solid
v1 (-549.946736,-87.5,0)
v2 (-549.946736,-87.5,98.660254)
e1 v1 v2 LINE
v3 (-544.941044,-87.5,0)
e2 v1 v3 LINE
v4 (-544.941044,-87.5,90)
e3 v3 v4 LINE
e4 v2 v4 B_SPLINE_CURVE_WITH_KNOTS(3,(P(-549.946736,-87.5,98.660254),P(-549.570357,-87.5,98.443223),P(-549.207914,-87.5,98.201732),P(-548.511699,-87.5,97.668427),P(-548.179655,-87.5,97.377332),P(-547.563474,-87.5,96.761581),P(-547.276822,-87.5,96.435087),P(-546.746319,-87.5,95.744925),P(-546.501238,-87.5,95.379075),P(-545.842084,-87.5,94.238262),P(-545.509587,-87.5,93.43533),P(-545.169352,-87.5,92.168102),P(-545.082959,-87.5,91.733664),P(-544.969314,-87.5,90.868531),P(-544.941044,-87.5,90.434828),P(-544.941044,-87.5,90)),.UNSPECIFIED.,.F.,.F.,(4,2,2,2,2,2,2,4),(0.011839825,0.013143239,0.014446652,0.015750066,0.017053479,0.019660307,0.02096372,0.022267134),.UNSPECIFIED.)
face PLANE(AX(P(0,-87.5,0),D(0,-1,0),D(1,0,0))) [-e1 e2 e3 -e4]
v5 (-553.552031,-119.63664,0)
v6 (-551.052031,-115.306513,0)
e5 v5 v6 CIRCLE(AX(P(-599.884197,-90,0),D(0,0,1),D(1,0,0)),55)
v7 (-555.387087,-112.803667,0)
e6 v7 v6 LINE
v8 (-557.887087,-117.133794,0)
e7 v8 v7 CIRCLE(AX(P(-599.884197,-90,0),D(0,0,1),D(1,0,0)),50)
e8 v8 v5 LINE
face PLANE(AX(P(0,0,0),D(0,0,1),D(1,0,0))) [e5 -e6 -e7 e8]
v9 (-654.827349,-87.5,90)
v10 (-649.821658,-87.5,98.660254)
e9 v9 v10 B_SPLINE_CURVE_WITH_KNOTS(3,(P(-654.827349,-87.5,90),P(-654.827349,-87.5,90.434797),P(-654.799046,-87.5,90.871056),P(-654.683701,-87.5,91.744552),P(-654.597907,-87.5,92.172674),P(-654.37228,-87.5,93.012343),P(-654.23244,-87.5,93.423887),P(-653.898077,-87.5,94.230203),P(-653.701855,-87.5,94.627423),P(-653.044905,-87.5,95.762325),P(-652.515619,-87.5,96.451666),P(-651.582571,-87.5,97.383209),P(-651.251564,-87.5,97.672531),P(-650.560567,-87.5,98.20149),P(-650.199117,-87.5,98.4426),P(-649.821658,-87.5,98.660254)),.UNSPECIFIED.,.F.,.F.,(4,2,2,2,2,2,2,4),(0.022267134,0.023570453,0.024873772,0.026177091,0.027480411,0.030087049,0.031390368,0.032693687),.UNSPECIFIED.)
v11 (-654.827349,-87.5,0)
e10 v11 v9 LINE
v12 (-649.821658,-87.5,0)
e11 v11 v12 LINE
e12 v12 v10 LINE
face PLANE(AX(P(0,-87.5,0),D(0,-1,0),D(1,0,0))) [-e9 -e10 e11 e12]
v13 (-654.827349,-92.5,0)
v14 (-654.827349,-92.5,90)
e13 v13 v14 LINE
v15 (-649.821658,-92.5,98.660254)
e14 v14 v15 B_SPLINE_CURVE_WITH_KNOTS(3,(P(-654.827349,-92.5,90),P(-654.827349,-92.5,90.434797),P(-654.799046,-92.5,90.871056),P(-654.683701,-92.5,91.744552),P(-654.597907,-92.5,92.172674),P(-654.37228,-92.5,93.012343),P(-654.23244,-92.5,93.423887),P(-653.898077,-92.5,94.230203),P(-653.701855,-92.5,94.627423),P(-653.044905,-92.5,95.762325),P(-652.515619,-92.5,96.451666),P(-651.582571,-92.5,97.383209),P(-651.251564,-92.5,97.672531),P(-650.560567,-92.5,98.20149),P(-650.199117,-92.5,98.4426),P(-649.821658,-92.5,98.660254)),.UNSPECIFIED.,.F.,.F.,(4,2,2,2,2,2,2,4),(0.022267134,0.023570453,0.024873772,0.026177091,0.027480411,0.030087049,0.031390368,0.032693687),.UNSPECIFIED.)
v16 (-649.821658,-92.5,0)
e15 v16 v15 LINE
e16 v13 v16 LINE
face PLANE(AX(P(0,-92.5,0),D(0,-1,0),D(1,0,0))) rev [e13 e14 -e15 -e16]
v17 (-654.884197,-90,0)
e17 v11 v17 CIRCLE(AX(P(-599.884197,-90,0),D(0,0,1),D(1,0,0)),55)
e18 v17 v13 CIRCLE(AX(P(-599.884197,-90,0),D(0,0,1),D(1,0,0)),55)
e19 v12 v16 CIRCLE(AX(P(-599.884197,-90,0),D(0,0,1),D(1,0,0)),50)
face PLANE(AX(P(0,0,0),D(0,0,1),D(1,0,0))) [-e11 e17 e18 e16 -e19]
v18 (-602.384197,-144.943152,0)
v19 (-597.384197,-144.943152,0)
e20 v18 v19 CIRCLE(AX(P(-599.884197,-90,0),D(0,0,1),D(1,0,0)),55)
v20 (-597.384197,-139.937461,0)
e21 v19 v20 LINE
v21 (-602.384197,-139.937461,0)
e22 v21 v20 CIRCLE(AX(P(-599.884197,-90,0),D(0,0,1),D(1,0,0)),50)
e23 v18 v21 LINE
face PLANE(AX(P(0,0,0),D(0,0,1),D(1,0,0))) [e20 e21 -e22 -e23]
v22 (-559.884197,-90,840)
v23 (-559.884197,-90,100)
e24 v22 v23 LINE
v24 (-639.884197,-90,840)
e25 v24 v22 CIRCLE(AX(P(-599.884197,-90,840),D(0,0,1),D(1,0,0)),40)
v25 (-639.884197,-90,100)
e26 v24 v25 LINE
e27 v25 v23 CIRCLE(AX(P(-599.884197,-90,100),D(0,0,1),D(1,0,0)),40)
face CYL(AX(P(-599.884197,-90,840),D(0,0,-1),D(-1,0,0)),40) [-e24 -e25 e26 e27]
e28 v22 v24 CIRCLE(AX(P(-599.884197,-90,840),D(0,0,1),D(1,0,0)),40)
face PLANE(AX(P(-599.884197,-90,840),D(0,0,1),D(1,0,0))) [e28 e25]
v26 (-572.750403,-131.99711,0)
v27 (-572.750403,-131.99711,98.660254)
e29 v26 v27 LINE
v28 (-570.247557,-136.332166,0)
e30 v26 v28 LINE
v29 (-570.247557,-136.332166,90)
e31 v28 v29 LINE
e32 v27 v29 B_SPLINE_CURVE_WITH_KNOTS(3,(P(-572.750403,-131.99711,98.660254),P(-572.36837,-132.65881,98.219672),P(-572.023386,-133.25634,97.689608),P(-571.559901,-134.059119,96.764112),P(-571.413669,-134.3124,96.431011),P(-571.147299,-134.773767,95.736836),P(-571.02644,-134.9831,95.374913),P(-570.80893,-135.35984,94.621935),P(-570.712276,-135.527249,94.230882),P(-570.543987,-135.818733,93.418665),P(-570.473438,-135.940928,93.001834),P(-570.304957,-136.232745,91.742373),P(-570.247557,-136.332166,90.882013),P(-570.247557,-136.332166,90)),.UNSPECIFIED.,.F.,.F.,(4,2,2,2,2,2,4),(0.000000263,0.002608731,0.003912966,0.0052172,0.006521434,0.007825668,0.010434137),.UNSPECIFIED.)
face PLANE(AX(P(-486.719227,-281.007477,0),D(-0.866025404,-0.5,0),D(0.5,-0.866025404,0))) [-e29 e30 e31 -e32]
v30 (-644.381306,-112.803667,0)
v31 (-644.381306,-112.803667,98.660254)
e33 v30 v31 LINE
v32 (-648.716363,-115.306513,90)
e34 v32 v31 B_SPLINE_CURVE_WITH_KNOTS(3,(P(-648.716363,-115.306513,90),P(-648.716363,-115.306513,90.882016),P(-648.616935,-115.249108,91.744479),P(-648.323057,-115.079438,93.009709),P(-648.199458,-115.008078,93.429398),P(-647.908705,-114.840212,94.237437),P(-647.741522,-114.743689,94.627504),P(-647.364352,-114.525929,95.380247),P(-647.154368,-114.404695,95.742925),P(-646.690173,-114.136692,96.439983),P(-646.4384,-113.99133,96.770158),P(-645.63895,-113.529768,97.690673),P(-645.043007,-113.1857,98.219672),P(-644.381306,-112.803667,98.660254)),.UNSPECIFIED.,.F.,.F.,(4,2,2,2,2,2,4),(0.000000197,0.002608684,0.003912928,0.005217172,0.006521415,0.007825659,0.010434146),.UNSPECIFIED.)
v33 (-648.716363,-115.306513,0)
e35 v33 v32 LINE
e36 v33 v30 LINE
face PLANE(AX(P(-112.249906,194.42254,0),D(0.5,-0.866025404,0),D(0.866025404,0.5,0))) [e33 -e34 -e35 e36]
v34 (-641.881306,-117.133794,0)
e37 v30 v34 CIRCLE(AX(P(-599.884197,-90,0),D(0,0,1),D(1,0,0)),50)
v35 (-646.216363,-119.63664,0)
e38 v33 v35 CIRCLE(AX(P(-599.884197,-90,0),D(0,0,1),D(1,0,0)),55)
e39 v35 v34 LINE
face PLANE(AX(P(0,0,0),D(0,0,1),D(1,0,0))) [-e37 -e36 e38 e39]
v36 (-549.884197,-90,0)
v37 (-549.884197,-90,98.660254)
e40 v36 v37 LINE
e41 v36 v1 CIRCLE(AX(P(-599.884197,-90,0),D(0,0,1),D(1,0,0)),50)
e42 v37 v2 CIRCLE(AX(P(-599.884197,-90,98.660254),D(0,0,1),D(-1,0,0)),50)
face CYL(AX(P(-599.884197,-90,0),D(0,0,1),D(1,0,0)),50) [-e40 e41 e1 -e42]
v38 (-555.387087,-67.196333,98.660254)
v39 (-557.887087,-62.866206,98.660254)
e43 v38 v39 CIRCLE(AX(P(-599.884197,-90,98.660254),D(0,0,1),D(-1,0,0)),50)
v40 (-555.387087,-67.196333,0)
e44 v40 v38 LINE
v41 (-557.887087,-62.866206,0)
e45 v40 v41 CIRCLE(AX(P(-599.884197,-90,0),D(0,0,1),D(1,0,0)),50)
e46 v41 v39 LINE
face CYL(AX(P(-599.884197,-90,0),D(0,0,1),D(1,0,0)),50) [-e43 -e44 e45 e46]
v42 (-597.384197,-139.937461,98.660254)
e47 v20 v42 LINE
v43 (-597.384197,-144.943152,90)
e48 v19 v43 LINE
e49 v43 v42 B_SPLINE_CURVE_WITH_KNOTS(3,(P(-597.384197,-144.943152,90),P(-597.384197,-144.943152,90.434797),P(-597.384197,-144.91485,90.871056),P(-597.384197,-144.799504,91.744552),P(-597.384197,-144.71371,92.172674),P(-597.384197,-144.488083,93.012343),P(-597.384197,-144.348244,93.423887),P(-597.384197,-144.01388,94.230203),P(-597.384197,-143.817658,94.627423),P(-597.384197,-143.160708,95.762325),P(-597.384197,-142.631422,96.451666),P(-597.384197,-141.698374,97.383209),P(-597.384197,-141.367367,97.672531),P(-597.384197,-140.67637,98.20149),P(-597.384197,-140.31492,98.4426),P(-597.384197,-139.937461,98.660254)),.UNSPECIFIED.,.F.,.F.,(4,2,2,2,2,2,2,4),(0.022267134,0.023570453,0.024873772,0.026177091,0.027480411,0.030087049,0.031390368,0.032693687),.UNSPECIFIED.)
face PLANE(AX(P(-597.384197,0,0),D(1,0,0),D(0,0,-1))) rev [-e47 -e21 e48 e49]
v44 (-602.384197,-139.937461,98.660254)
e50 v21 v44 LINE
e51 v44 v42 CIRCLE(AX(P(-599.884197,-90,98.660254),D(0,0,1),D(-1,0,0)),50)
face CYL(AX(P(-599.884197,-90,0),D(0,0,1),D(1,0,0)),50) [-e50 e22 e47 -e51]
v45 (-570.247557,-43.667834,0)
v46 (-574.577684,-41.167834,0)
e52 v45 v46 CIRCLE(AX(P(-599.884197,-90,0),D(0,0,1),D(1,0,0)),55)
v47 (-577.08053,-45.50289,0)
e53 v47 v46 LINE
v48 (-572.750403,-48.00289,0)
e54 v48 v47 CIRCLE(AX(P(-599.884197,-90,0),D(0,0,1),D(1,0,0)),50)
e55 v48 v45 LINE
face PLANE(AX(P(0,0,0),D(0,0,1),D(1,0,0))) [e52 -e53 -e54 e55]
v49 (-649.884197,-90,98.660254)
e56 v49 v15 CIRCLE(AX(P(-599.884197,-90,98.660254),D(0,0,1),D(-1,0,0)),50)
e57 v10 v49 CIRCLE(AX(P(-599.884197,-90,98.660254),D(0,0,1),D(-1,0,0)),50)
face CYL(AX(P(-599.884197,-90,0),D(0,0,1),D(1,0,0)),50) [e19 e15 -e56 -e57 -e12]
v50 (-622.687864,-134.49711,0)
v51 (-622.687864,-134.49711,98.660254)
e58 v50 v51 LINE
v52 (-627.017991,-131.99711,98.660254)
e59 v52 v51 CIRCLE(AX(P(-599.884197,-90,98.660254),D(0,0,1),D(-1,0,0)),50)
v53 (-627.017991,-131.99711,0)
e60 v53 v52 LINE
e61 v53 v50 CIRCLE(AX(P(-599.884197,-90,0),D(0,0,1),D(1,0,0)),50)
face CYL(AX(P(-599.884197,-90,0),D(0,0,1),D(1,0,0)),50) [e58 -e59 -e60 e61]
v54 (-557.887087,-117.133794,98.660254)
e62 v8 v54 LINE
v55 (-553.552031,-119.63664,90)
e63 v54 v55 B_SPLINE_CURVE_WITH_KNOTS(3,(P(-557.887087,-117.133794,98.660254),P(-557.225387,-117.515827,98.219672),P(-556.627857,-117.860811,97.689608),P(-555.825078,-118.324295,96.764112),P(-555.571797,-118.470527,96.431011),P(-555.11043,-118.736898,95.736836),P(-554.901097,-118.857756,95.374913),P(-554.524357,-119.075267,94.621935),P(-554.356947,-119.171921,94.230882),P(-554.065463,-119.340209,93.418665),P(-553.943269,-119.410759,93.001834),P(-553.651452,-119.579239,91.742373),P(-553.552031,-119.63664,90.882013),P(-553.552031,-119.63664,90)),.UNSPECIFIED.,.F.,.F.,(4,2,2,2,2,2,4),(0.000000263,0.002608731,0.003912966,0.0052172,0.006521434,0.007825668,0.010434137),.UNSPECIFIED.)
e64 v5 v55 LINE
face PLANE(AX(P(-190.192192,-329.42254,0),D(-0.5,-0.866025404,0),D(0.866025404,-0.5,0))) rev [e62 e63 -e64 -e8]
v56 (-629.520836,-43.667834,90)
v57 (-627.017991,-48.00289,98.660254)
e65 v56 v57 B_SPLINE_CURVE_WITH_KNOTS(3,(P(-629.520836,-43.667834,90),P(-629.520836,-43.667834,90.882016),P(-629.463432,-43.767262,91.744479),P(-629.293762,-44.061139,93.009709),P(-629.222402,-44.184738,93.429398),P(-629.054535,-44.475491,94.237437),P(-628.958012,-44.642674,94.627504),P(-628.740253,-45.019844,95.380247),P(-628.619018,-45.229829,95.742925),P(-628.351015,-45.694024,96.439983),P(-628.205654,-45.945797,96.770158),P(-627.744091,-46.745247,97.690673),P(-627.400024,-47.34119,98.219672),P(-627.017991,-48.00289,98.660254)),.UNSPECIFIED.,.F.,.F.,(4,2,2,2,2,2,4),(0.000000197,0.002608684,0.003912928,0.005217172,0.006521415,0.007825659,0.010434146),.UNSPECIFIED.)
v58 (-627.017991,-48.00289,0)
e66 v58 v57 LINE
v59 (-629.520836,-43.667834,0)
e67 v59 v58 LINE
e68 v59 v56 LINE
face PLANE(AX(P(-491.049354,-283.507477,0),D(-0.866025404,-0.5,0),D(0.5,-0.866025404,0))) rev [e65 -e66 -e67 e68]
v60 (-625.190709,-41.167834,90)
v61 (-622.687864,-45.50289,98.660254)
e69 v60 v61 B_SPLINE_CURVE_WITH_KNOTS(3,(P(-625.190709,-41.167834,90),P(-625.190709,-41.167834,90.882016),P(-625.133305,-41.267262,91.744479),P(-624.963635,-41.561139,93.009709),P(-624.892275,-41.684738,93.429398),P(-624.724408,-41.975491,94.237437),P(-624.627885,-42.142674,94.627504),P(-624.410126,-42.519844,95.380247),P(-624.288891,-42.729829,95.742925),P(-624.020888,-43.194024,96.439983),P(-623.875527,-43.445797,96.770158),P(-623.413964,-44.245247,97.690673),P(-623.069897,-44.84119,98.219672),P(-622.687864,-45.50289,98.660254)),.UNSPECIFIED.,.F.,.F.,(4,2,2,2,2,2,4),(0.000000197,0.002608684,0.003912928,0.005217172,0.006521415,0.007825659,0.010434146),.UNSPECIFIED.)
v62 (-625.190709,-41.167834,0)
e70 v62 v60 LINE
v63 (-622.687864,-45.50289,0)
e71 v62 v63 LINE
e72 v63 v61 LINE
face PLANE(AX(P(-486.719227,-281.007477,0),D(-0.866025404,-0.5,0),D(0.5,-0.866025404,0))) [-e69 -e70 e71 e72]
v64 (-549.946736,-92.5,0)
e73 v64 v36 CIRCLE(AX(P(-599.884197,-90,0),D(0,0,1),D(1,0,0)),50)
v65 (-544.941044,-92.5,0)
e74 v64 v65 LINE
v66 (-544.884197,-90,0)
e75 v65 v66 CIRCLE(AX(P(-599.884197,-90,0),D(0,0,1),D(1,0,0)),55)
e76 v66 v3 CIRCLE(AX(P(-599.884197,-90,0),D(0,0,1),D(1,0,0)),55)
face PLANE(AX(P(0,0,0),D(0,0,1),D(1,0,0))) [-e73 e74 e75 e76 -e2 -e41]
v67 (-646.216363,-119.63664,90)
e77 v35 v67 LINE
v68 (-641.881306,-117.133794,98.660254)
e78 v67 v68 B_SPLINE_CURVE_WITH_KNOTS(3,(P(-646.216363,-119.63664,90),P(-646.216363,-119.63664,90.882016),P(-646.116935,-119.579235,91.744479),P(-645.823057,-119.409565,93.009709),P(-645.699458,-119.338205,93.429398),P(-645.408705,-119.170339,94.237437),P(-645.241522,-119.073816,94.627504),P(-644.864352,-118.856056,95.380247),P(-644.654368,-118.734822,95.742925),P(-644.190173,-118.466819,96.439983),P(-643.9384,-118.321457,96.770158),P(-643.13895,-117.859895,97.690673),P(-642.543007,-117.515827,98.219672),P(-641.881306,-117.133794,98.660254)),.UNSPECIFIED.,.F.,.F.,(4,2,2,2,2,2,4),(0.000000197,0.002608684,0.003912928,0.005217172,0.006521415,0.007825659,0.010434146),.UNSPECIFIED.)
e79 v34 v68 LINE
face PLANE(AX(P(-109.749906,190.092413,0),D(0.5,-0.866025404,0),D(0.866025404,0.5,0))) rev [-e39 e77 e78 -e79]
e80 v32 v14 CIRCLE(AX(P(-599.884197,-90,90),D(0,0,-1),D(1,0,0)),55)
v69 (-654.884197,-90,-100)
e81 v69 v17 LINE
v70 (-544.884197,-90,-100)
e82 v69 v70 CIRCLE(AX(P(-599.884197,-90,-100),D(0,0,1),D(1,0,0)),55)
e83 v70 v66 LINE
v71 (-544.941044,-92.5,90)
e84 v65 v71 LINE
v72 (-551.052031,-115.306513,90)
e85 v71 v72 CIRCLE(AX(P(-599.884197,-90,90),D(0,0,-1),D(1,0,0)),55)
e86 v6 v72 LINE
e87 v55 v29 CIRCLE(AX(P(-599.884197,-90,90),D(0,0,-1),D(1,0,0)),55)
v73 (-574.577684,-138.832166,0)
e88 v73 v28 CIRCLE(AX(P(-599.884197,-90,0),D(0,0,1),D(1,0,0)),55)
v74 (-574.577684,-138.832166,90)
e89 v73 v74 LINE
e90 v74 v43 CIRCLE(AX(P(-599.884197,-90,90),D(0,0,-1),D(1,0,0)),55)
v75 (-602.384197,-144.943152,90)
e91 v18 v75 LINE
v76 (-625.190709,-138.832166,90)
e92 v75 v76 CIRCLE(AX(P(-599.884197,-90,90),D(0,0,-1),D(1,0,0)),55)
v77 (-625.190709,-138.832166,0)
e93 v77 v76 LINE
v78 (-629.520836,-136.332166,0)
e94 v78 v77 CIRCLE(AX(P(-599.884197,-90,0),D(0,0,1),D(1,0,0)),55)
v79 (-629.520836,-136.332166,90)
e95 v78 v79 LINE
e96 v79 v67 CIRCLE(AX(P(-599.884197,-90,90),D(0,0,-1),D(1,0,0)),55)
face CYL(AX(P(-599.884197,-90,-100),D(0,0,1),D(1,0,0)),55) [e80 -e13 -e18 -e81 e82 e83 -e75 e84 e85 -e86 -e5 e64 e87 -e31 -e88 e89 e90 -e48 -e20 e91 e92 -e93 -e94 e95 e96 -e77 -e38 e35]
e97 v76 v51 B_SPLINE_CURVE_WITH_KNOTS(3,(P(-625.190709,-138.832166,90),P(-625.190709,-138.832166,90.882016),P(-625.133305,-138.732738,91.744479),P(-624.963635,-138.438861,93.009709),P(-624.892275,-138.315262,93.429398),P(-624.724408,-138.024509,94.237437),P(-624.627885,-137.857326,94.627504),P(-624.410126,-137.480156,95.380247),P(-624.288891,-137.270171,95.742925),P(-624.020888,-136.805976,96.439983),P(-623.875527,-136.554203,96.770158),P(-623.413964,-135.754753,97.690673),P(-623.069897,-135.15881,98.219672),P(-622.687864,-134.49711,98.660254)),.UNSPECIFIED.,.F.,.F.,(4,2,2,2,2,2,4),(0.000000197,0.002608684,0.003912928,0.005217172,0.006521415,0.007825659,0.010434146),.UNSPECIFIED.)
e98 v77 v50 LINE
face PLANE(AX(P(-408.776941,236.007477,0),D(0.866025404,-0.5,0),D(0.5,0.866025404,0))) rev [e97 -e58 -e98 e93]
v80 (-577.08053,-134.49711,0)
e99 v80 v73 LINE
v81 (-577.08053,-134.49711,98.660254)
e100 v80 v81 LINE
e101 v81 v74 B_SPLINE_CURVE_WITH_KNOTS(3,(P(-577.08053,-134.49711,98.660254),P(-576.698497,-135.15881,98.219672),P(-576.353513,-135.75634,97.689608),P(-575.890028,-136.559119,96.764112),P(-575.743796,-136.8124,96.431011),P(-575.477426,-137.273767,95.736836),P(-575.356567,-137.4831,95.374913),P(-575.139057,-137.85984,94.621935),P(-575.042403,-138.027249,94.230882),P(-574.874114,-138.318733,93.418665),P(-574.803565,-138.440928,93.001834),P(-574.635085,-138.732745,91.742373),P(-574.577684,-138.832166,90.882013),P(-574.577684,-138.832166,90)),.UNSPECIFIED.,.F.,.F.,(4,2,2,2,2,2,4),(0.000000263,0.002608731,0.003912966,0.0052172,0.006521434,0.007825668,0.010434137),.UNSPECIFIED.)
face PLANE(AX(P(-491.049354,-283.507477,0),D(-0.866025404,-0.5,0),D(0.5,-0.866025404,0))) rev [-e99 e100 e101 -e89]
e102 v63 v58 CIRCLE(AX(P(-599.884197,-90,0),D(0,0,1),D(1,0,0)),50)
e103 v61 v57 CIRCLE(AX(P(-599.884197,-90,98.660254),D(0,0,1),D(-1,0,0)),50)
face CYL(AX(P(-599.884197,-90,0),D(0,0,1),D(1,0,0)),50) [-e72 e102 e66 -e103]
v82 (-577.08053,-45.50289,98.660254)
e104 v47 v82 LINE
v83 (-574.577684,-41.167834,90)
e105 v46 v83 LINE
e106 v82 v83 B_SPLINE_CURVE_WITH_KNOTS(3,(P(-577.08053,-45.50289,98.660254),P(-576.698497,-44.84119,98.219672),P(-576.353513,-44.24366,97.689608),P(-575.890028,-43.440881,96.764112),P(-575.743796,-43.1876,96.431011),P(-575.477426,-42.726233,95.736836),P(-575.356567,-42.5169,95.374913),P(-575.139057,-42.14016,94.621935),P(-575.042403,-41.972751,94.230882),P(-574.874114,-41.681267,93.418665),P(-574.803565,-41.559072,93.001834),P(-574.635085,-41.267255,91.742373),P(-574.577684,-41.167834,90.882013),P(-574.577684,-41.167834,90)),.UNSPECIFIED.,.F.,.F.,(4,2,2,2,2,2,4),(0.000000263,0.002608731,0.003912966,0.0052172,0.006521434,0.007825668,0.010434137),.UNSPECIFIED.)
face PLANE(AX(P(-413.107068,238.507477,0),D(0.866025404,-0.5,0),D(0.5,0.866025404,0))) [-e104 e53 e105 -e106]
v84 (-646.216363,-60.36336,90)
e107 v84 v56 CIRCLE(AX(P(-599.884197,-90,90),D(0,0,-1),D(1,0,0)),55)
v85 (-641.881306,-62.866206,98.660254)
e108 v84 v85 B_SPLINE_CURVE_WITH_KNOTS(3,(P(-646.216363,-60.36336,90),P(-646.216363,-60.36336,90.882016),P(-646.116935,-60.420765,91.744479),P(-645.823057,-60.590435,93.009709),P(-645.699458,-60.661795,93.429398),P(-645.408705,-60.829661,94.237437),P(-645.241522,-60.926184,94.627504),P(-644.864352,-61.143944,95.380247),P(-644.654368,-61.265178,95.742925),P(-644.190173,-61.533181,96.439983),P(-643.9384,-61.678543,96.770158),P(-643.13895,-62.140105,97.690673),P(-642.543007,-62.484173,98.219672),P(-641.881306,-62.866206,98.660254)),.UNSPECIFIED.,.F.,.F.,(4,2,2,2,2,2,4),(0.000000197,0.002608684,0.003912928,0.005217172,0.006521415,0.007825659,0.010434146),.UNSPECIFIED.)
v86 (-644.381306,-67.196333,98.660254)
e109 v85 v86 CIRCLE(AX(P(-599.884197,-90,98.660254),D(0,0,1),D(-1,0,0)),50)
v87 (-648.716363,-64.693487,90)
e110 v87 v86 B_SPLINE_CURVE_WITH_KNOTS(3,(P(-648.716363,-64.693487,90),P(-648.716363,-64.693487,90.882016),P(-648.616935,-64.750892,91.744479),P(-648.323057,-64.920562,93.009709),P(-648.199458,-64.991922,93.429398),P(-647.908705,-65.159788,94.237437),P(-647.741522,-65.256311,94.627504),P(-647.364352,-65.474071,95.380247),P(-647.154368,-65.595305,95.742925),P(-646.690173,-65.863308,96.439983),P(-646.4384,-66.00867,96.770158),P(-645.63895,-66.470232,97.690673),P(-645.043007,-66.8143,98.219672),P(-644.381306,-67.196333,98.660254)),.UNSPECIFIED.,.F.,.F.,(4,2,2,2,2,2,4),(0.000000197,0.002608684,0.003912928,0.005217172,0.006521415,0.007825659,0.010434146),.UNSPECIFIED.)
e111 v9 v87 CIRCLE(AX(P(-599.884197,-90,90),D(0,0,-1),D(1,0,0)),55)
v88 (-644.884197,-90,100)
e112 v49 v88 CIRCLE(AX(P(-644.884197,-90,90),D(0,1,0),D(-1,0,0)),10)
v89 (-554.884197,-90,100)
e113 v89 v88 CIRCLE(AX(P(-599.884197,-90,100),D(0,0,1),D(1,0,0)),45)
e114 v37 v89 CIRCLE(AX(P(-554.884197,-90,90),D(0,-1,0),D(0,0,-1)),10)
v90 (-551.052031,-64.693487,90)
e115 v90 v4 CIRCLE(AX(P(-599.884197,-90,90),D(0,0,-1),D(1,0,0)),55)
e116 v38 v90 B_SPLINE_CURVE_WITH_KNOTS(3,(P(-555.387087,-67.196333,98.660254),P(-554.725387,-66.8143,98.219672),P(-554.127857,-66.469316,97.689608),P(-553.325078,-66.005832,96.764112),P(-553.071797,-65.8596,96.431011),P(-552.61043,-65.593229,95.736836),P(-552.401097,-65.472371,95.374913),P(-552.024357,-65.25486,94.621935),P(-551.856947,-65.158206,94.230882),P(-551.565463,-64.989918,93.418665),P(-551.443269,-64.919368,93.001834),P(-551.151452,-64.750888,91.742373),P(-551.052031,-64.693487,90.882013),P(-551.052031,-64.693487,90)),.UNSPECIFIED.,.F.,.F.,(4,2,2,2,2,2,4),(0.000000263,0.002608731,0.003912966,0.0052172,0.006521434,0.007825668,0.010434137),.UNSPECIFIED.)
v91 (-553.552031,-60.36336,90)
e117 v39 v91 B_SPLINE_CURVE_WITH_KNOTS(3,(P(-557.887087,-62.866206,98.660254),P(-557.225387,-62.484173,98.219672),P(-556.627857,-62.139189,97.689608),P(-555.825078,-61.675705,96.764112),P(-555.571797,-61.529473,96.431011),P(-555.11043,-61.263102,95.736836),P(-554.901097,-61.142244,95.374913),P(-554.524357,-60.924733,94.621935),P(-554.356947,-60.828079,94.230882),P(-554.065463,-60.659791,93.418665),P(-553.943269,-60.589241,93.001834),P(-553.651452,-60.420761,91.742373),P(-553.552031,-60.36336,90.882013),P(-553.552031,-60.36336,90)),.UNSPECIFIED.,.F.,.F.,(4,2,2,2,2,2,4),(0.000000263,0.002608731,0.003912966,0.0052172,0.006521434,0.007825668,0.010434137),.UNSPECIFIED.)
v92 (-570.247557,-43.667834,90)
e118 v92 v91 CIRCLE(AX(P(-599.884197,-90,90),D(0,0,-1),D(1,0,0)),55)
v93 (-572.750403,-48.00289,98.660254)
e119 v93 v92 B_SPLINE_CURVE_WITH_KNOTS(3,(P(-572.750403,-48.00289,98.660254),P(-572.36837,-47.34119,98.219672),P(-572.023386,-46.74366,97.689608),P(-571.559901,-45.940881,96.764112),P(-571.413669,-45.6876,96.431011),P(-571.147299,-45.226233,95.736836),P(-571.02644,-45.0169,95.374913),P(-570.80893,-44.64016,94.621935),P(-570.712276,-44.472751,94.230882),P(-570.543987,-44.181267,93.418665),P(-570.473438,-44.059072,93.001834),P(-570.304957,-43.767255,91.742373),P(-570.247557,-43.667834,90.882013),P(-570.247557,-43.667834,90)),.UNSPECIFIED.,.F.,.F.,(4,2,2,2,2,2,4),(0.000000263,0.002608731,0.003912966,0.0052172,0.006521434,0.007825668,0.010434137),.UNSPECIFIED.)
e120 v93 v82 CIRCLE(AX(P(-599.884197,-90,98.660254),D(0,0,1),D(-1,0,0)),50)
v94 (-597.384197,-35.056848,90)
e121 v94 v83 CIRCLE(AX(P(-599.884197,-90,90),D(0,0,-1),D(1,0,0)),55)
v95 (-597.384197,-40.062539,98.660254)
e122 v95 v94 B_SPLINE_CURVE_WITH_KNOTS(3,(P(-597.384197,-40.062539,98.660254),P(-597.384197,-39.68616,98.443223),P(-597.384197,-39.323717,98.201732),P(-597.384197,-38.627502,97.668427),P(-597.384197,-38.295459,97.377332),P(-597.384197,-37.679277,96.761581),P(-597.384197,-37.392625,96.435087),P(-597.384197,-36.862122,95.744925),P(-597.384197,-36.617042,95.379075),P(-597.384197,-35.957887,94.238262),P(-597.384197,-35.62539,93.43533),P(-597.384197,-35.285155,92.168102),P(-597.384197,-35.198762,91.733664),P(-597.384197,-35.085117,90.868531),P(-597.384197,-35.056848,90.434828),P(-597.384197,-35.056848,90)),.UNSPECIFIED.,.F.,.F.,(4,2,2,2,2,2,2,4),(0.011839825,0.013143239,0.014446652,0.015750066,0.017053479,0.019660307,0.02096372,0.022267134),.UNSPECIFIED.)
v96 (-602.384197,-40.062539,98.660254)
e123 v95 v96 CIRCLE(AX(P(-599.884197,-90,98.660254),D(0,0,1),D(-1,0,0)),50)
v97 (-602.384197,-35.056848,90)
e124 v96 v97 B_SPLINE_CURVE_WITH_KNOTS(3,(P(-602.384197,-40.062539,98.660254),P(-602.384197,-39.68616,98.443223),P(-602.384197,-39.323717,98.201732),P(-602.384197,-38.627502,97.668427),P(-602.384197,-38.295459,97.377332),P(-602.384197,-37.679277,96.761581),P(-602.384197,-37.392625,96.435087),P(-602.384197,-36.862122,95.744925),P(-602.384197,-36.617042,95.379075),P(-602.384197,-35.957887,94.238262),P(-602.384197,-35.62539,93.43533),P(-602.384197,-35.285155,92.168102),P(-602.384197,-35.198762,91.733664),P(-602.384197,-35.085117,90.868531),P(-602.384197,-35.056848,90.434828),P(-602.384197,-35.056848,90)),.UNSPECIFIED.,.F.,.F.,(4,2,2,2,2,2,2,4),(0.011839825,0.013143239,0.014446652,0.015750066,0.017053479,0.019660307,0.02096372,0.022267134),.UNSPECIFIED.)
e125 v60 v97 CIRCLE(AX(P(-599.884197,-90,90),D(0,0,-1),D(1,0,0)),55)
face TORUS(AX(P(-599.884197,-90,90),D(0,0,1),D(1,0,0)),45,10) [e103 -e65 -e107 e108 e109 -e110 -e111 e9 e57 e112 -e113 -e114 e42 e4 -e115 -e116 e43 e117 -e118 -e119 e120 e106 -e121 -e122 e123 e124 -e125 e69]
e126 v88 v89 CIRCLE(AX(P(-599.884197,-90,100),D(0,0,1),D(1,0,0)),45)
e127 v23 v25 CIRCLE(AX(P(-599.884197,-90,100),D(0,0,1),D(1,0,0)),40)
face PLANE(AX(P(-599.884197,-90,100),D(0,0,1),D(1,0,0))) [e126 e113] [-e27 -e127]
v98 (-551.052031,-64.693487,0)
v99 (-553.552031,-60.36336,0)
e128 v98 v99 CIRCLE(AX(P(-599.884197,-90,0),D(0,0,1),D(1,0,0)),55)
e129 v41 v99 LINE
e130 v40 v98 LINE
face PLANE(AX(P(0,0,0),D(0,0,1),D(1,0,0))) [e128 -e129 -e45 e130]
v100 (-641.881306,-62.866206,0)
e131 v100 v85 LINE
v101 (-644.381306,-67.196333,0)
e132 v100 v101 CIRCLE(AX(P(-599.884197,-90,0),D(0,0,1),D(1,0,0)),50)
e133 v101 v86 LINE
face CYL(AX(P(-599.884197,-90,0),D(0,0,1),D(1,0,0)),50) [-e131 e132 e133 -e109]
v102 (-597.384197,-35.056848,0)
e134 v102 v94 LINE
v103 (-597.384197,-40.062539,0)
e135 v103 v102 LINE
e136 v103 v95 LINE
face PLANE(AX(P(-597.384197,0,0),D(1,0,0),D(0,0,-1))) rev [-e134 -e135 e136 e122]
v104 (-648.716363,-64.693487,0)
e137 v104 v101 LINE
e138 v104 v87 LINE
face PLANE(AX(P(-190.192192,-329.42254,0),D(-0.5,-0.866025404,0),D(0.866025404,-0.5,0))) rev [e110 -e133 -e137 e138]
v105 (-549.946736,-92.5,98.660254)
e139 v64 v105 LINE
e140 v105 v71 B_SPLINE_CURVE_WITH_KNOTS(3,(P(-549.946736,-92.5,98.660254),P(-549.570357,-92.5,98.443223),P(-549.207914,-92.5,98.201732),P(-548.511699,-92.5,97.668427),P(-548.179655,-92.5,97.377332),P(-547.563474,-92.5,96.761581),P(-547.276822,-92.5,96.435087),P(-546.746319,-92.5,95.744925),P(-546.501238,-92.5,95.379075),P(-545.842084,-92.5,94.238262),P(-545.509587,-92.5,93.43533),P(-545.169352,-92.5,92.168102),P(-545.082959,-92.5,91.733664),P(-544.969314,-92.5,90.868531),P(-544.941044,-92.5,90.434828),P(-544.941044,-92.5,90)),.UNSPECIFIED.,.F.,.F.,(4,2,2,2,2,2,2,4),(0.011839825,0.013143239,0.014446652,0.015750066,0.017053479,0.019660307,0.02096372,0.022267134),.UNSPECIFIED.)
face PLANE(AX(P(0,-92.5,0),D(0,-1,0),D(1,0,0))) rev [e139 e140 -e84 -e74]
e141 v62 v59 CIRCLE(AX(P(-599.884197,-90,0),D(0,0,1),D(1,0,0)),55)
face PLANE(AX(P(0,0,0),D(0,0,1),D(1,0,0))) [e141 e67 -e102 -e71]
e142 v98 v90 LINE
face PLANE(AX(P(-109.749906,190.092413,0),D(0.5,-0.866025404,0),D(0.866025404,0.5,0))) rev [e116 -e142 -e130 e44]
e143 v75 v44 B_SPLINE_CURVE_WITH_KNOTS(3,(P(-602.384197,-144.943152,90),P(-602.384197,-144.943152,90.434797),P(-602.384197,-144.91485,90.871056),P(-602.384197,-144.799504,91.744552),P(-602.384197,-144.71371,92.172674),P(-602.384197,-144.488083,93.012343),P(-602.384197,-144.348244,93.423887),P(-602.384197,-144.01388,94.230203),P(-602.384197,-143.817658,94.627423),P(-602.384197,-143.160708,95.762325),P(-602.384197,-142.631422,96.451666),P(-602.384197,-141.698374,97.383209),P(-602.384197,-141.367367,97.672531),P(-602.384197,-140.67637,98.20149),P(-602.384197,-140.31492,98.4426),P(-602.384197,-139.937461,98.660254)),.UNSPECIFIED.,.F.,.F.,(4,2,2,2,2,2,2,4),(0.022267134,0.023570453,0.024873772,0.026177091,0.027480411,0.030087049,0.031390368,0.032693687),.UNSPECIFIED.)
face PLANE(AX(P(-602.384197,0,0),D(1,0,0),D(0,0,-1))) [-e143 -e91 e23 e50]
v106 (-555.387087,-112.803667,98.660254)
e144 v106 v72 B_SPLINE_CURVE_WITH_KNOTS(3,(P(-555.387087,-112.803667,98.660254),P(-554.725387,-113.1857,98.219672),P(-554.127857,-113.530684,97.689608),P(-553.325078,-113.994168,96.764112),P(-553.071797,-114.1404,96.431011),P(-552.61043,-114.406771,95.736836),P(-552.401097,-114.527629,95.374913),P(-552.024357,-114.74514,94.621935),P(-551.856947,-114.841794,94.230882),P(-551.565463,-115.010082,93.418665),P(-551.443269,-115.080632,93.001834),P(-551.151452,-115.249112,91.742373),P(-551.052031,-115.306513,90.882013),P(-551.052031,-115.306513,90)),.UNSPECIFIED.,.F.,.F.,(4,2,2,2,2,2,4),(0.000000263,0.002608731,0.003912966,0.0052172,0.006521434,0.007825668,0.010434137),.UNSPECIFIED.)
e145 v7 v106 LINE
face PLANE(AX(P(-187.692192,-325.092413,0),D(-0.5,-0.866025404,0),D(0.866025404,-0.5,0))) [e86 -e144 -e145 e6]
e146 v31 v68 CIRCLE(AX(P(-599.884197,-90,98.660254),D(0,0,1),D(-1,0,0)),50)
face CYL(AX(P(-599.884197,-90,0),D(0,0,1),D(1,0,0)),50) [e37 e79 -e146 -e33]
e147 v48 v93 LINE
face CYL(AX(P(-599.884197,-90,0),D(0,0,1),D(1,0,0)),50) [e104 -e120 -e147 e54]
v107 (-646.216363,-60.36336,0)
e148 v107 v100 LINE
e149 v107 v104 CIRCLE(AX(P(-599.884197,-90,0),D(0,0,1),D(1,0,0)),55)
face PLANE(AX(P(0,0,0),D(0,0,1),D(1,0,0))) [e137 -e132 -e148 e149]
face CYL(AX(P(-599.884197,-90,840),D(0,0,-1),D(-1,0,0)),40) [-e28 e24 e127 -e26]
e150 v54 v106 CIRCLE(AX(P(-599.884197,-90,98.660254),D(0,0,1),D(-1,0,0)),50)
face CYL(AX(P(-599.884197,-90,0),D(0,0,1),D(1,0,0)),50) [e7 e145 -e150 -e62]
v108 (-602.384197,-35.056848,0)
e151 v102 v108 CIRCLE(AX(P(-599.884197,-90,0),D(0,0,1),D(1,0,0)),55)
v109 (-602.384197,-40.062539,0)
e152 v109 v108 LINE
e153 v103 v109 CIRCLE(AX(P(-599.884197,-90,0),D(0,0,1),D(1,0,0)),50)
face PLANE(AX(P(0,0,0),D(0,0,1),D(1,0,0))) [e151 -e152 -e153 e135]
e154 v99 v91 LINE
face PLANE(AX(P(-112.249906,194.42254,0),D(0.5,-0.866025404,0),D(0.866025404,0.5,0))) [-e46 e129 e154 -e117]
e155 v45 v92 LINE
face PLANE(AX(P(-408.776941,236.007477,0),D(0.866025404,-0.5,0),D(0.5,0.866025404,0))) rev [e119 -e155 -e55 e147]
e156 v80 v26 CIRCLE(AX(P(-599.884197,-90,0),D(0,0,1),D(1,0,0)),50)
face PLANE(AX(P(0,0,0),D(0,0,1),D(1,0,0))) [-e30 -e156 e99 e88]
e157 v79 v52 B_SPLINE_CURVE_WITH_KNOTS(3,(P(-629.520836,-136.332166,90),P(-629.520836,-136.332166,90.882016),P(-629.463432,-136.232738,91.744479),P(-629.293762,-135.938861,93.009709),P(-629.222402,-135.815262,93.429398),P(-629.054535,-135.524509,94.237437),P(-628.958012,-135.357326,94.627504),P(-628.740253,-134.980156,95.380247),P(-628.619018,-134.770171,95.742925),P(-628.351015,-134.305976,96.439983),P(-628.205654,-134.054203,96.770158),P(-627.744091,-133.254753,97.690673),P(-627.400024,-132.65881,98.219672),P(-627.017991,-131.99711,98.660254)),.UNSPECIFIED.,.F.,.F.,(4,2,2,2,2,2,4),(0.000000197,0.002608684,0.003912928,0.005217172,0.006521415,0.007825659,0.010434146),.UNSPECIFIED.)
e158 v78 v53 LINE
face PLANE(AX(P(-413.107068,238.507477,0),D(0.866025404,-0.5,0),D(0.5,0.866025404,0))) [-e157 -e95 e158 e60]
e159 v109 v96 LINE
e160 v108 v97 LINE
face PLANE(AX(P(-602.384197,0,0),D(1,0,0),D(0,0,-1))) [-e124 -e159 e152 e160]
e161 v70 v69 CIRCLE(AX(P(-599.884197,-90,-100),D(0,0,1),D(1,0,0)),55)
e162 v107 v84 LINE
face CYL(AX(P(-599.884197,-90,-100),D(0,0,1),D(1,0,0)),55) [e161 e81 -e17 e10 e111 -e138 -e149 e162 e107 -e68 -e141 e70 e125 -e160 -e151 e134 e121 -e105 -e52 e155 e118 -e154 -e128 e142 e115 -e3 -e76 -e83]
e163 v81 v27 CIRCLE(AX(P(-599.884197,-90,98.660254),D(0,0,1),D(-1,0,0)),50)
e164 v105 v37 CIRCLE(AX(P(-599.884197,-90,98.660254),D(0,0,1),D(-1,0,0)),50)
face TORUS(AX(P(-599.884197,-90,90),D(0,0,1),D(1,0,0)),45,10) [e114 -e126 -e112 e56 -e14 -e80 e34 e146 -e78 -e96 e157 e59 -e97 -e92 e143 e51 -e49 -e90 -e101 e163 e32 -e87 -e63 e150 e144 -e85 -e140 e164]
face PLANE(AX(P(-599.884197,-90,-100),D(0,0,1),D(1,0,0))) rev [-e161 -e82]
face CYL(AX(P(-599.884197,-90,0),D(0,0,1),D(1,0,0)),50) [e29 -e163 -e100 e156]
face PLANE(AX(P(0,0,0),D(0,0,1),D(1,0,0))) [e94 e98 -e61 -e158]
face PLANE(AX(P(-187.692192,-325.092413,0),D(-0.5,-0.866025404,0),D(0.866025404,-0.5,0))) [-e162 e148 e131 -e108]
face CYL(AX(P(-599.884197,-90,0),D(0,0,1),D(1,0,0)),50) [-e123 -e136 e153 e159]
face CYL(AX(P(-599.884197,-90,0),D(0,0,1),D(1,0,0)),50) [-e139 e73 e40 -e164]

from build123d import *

# Parameters (mm, degrees)
BOSS_EXTRUDE1_DEPTH      = 100
BOSS_EXTRUDE1_DEPTH_BACK = 100
SKETCH1_R                = 55
FILLET1_R                = 10
CUT_EXTRUDE1_DEPTH       = 100
SKETCH3_R                = 40
BOSS_EXTRUDE2_DEPTH      = 740


with BuildPart() as part:
    # Sketch1 → Boss-Extrude1 (new, two sides: drawn at the far end of the back side and taken through both)
    with BuildSketch(Plane.XY.offset(-BOSS_EXTRUDE1_DEPTH_BACK)):
        with Locations((-599.884196758, -90)):
            Circle(SKETCH1_R)
    extrude(amount=BOSS_EXTRUDE1_DEPTH + BOSS_EXTRUDE1_DEPTH_BACK)

    # Fillet1
    fillet1_edges = [part.edges().sort_by_distance(p)[0] for p in [
        (-654.884196758, -90, 100),
    ]]
    fillet(fillet1_edges, radius=FILLET1_R)

    # Sketch2 → Cut-Extrude1 (cut)
    with BuildSketch(Plane.XY.offset(100)):
        with BuildLine():
            Line((-627.017990712, -131.99710973), (-629.520836487, -136.332165777))
            ThreePointArc((-629.520836487, -136.332165777), (-627.384196758, -137.631397208), (-625.190709468, -138.832165777))
            Line((-625.190709468, -138.832165777), (-622.687863693, -134.49710973))
            ThreePointArc((-622.687863693, -134.49710973), (-624.884196758, -133.301270189), (-627.017990712, -131.99710973))
        make_face()
        with BuildLine():
            ThreePointArc((-648.716362535, -115.30651271), (-647.515593966, -117.5), (-646.216362535, -119.636639729))
            Line((-646.216362535, -119.636639729), (-641.881306488, -117.133793954))
            ThreePointArc((-641.881306488, -117.133793954), (-643.185466947, -115), (-644.381306488, -112.803666935))
            Line((-644.381306488, -112.803666935), (-648.716362535, -115.30651271))
        make_face()
        with BuildLine():
            Line((-602.384196758, -139.937460889), (-602.384196758, -144.94315244))
            ThreePointArc((-602.384196758, -144.94315244), (-599.884196758, -145), (-597.384196758, -144.94315244))
            Line((-597.384196758, -144.94315244), (-597.384196758, -139.937460889))
            ThreePointArc((-597.384196758, -139.937460889), (-599.884196758, -140), (-602.384196758, -139.937460889))
        make_face()
        with BuildLine():
            ThreePointArc((-654.827349198, -87.5), (-654.884196758, -90), (-654.827349198, -92.5))
            Line((-654.827349198, -92.5), (-649.821657647, -92.5))
            ThreePointArc((-649.821657647, -92.5), (-649.884196758, -90), (-649.821657647, -87.5))
            Line((-649.821657647, -87.5), (-654.827349198, -87.5))
        make_face()
        with BuildLine():
            Line((-577.080529823, -134.49710973), (-574.577684048, -138.832165777))
            ThreePointArc((-574.577684048, -138.832165777), (-572.384196758, -137.631397208), (-570.247557029, -136.332165777))
            Line((-570.247557029, -136.332165777), (-572.750402804, -131.99710973))
            ThreePointArc((-572.750402804, -131.99710973), (-574.884196758, -133.301270189), (-577.080529823, -134.49710973))
        make_face()
        with BuildLine():
            ThreePointArc((-646.216362535, -60.363360271), (-647.515593966, -62.5), (-648.716362535, -64.69348729))
            Line((-648.716362535, -64.69348729), (-644.381306488, -67.196333065))
            ThreePointArc((-644.381306488, -67.196333065), (-643.185466947, -65), (-641.881306488, -62.866206046))
            Line((-641.881306488, -62.866206046), (-646.216362535, -60.363360271))
        make_face()
        with BuildLine():
            Line((-557.887087028, -117.133793954), (-553.552030981, -119.636639729))
            ThreePointArc((-553.552030981, -119.636639729), (-552.25279955, -117.5), (-551.052030981, -115.30651271))
            Line((-551.052030981, -115.30651271), (-555.387087028, -112.803666935))
            ThreePointArc((-555.387087028, -112.803666935), (-556.582926569, -115), (-557.887087028, -117.133793954))
        make_face()
        with BuildLine():
            ThreePointArc((-625.190709468, -41.167834223), (-627.384196758, -42.368602792), (-629.520836487, -43.667834223))
            Line((-629.520836487, -43.667834223), (-627.017990712, -48.00289027))
            ThreePointArc((-627.017990712, -48.00289027), (-624.884196758, -46.698729811), (-622.687863693, -45.50289027))
            Line((-622.687863693, -45.50289027), (-625.190709468, -41.167834223))
        make_face()
        with BuildLine():
            Line((-549.946735869, -92.5), (-544.941044318, -92.5))
            ThreePointArc((-544.941044318, -92.5), (-544.884196758, -90), (-544.941044318, -87.5))
            Line((-544.941044318, -87.5), (-549.946735869, -87.5))
            ThreePointArc((-549.946735869, -87.5), (-549.884196758, -90), (-549.946735869, -92.5))
        make_face()
        with BuildLine():
            ThreePointArc((-597.384196758, -35.05684756), (-599.884196758, -35), (-602.384196758, -35.05684756))
            Line((-602.384196758, -35.05684756), (-602.384196758, -40.062539111))
            ThreePointArc((-602.384196758, -40.062539111), (-599.884196758, -40), (-597.384196758, -40.062539111))
            Line((-597.384196758, -40.062539111), (-597.384196758, -35.05684756))
        make_face()
        with BuildLine():
            ThreePointArc((-570.247557029, -43.667834223), (-572.384196758, -42.368602792), (-574.577684048, -41.167834223))
            Line((-574.577684048, -41.167834223), (-577.080529823, -45.50289027))
            ThreePointArc((-577.080529823, -45.50289027), (-574.884196758, -46.698729811), (-572.750402804, -48.00289027))
            Line((-572.750402804, -48.00289027), (-570.247557029, -43.667834223))
        make_face()
        with BuildLine():
            Line((-555.387087028, -67.196333065), (-551.052030981, -64.69348729))
            ThreePointArc((-551.052030981, -64.69348729), (-552.25279955, -62.5), (-553.552030981, -60.363360271))
            Line((-553.552030981, -60.363360271), (-557.887087028, -62.866206046))
            ThreePointArc((-557.887087028, -62.866206046), (-556.582926569, -65), (-555.387087028, -67.196333065))
        make_face()
    extrude(amount=-CUT_EXTRUDE1_DEPTH, mode=Mode.SUBTRACT)

    # Sketch3 → Boss-Extrude2 (add)
    with BuildSketch(Plane.XY.offset(100)):
        with Locations((-599.884196758, -90)):
            Circle(SKETCH3_R)
    extrude(amount=BOSS_EXTRUDE2_DEPTH)


solid = part.part
